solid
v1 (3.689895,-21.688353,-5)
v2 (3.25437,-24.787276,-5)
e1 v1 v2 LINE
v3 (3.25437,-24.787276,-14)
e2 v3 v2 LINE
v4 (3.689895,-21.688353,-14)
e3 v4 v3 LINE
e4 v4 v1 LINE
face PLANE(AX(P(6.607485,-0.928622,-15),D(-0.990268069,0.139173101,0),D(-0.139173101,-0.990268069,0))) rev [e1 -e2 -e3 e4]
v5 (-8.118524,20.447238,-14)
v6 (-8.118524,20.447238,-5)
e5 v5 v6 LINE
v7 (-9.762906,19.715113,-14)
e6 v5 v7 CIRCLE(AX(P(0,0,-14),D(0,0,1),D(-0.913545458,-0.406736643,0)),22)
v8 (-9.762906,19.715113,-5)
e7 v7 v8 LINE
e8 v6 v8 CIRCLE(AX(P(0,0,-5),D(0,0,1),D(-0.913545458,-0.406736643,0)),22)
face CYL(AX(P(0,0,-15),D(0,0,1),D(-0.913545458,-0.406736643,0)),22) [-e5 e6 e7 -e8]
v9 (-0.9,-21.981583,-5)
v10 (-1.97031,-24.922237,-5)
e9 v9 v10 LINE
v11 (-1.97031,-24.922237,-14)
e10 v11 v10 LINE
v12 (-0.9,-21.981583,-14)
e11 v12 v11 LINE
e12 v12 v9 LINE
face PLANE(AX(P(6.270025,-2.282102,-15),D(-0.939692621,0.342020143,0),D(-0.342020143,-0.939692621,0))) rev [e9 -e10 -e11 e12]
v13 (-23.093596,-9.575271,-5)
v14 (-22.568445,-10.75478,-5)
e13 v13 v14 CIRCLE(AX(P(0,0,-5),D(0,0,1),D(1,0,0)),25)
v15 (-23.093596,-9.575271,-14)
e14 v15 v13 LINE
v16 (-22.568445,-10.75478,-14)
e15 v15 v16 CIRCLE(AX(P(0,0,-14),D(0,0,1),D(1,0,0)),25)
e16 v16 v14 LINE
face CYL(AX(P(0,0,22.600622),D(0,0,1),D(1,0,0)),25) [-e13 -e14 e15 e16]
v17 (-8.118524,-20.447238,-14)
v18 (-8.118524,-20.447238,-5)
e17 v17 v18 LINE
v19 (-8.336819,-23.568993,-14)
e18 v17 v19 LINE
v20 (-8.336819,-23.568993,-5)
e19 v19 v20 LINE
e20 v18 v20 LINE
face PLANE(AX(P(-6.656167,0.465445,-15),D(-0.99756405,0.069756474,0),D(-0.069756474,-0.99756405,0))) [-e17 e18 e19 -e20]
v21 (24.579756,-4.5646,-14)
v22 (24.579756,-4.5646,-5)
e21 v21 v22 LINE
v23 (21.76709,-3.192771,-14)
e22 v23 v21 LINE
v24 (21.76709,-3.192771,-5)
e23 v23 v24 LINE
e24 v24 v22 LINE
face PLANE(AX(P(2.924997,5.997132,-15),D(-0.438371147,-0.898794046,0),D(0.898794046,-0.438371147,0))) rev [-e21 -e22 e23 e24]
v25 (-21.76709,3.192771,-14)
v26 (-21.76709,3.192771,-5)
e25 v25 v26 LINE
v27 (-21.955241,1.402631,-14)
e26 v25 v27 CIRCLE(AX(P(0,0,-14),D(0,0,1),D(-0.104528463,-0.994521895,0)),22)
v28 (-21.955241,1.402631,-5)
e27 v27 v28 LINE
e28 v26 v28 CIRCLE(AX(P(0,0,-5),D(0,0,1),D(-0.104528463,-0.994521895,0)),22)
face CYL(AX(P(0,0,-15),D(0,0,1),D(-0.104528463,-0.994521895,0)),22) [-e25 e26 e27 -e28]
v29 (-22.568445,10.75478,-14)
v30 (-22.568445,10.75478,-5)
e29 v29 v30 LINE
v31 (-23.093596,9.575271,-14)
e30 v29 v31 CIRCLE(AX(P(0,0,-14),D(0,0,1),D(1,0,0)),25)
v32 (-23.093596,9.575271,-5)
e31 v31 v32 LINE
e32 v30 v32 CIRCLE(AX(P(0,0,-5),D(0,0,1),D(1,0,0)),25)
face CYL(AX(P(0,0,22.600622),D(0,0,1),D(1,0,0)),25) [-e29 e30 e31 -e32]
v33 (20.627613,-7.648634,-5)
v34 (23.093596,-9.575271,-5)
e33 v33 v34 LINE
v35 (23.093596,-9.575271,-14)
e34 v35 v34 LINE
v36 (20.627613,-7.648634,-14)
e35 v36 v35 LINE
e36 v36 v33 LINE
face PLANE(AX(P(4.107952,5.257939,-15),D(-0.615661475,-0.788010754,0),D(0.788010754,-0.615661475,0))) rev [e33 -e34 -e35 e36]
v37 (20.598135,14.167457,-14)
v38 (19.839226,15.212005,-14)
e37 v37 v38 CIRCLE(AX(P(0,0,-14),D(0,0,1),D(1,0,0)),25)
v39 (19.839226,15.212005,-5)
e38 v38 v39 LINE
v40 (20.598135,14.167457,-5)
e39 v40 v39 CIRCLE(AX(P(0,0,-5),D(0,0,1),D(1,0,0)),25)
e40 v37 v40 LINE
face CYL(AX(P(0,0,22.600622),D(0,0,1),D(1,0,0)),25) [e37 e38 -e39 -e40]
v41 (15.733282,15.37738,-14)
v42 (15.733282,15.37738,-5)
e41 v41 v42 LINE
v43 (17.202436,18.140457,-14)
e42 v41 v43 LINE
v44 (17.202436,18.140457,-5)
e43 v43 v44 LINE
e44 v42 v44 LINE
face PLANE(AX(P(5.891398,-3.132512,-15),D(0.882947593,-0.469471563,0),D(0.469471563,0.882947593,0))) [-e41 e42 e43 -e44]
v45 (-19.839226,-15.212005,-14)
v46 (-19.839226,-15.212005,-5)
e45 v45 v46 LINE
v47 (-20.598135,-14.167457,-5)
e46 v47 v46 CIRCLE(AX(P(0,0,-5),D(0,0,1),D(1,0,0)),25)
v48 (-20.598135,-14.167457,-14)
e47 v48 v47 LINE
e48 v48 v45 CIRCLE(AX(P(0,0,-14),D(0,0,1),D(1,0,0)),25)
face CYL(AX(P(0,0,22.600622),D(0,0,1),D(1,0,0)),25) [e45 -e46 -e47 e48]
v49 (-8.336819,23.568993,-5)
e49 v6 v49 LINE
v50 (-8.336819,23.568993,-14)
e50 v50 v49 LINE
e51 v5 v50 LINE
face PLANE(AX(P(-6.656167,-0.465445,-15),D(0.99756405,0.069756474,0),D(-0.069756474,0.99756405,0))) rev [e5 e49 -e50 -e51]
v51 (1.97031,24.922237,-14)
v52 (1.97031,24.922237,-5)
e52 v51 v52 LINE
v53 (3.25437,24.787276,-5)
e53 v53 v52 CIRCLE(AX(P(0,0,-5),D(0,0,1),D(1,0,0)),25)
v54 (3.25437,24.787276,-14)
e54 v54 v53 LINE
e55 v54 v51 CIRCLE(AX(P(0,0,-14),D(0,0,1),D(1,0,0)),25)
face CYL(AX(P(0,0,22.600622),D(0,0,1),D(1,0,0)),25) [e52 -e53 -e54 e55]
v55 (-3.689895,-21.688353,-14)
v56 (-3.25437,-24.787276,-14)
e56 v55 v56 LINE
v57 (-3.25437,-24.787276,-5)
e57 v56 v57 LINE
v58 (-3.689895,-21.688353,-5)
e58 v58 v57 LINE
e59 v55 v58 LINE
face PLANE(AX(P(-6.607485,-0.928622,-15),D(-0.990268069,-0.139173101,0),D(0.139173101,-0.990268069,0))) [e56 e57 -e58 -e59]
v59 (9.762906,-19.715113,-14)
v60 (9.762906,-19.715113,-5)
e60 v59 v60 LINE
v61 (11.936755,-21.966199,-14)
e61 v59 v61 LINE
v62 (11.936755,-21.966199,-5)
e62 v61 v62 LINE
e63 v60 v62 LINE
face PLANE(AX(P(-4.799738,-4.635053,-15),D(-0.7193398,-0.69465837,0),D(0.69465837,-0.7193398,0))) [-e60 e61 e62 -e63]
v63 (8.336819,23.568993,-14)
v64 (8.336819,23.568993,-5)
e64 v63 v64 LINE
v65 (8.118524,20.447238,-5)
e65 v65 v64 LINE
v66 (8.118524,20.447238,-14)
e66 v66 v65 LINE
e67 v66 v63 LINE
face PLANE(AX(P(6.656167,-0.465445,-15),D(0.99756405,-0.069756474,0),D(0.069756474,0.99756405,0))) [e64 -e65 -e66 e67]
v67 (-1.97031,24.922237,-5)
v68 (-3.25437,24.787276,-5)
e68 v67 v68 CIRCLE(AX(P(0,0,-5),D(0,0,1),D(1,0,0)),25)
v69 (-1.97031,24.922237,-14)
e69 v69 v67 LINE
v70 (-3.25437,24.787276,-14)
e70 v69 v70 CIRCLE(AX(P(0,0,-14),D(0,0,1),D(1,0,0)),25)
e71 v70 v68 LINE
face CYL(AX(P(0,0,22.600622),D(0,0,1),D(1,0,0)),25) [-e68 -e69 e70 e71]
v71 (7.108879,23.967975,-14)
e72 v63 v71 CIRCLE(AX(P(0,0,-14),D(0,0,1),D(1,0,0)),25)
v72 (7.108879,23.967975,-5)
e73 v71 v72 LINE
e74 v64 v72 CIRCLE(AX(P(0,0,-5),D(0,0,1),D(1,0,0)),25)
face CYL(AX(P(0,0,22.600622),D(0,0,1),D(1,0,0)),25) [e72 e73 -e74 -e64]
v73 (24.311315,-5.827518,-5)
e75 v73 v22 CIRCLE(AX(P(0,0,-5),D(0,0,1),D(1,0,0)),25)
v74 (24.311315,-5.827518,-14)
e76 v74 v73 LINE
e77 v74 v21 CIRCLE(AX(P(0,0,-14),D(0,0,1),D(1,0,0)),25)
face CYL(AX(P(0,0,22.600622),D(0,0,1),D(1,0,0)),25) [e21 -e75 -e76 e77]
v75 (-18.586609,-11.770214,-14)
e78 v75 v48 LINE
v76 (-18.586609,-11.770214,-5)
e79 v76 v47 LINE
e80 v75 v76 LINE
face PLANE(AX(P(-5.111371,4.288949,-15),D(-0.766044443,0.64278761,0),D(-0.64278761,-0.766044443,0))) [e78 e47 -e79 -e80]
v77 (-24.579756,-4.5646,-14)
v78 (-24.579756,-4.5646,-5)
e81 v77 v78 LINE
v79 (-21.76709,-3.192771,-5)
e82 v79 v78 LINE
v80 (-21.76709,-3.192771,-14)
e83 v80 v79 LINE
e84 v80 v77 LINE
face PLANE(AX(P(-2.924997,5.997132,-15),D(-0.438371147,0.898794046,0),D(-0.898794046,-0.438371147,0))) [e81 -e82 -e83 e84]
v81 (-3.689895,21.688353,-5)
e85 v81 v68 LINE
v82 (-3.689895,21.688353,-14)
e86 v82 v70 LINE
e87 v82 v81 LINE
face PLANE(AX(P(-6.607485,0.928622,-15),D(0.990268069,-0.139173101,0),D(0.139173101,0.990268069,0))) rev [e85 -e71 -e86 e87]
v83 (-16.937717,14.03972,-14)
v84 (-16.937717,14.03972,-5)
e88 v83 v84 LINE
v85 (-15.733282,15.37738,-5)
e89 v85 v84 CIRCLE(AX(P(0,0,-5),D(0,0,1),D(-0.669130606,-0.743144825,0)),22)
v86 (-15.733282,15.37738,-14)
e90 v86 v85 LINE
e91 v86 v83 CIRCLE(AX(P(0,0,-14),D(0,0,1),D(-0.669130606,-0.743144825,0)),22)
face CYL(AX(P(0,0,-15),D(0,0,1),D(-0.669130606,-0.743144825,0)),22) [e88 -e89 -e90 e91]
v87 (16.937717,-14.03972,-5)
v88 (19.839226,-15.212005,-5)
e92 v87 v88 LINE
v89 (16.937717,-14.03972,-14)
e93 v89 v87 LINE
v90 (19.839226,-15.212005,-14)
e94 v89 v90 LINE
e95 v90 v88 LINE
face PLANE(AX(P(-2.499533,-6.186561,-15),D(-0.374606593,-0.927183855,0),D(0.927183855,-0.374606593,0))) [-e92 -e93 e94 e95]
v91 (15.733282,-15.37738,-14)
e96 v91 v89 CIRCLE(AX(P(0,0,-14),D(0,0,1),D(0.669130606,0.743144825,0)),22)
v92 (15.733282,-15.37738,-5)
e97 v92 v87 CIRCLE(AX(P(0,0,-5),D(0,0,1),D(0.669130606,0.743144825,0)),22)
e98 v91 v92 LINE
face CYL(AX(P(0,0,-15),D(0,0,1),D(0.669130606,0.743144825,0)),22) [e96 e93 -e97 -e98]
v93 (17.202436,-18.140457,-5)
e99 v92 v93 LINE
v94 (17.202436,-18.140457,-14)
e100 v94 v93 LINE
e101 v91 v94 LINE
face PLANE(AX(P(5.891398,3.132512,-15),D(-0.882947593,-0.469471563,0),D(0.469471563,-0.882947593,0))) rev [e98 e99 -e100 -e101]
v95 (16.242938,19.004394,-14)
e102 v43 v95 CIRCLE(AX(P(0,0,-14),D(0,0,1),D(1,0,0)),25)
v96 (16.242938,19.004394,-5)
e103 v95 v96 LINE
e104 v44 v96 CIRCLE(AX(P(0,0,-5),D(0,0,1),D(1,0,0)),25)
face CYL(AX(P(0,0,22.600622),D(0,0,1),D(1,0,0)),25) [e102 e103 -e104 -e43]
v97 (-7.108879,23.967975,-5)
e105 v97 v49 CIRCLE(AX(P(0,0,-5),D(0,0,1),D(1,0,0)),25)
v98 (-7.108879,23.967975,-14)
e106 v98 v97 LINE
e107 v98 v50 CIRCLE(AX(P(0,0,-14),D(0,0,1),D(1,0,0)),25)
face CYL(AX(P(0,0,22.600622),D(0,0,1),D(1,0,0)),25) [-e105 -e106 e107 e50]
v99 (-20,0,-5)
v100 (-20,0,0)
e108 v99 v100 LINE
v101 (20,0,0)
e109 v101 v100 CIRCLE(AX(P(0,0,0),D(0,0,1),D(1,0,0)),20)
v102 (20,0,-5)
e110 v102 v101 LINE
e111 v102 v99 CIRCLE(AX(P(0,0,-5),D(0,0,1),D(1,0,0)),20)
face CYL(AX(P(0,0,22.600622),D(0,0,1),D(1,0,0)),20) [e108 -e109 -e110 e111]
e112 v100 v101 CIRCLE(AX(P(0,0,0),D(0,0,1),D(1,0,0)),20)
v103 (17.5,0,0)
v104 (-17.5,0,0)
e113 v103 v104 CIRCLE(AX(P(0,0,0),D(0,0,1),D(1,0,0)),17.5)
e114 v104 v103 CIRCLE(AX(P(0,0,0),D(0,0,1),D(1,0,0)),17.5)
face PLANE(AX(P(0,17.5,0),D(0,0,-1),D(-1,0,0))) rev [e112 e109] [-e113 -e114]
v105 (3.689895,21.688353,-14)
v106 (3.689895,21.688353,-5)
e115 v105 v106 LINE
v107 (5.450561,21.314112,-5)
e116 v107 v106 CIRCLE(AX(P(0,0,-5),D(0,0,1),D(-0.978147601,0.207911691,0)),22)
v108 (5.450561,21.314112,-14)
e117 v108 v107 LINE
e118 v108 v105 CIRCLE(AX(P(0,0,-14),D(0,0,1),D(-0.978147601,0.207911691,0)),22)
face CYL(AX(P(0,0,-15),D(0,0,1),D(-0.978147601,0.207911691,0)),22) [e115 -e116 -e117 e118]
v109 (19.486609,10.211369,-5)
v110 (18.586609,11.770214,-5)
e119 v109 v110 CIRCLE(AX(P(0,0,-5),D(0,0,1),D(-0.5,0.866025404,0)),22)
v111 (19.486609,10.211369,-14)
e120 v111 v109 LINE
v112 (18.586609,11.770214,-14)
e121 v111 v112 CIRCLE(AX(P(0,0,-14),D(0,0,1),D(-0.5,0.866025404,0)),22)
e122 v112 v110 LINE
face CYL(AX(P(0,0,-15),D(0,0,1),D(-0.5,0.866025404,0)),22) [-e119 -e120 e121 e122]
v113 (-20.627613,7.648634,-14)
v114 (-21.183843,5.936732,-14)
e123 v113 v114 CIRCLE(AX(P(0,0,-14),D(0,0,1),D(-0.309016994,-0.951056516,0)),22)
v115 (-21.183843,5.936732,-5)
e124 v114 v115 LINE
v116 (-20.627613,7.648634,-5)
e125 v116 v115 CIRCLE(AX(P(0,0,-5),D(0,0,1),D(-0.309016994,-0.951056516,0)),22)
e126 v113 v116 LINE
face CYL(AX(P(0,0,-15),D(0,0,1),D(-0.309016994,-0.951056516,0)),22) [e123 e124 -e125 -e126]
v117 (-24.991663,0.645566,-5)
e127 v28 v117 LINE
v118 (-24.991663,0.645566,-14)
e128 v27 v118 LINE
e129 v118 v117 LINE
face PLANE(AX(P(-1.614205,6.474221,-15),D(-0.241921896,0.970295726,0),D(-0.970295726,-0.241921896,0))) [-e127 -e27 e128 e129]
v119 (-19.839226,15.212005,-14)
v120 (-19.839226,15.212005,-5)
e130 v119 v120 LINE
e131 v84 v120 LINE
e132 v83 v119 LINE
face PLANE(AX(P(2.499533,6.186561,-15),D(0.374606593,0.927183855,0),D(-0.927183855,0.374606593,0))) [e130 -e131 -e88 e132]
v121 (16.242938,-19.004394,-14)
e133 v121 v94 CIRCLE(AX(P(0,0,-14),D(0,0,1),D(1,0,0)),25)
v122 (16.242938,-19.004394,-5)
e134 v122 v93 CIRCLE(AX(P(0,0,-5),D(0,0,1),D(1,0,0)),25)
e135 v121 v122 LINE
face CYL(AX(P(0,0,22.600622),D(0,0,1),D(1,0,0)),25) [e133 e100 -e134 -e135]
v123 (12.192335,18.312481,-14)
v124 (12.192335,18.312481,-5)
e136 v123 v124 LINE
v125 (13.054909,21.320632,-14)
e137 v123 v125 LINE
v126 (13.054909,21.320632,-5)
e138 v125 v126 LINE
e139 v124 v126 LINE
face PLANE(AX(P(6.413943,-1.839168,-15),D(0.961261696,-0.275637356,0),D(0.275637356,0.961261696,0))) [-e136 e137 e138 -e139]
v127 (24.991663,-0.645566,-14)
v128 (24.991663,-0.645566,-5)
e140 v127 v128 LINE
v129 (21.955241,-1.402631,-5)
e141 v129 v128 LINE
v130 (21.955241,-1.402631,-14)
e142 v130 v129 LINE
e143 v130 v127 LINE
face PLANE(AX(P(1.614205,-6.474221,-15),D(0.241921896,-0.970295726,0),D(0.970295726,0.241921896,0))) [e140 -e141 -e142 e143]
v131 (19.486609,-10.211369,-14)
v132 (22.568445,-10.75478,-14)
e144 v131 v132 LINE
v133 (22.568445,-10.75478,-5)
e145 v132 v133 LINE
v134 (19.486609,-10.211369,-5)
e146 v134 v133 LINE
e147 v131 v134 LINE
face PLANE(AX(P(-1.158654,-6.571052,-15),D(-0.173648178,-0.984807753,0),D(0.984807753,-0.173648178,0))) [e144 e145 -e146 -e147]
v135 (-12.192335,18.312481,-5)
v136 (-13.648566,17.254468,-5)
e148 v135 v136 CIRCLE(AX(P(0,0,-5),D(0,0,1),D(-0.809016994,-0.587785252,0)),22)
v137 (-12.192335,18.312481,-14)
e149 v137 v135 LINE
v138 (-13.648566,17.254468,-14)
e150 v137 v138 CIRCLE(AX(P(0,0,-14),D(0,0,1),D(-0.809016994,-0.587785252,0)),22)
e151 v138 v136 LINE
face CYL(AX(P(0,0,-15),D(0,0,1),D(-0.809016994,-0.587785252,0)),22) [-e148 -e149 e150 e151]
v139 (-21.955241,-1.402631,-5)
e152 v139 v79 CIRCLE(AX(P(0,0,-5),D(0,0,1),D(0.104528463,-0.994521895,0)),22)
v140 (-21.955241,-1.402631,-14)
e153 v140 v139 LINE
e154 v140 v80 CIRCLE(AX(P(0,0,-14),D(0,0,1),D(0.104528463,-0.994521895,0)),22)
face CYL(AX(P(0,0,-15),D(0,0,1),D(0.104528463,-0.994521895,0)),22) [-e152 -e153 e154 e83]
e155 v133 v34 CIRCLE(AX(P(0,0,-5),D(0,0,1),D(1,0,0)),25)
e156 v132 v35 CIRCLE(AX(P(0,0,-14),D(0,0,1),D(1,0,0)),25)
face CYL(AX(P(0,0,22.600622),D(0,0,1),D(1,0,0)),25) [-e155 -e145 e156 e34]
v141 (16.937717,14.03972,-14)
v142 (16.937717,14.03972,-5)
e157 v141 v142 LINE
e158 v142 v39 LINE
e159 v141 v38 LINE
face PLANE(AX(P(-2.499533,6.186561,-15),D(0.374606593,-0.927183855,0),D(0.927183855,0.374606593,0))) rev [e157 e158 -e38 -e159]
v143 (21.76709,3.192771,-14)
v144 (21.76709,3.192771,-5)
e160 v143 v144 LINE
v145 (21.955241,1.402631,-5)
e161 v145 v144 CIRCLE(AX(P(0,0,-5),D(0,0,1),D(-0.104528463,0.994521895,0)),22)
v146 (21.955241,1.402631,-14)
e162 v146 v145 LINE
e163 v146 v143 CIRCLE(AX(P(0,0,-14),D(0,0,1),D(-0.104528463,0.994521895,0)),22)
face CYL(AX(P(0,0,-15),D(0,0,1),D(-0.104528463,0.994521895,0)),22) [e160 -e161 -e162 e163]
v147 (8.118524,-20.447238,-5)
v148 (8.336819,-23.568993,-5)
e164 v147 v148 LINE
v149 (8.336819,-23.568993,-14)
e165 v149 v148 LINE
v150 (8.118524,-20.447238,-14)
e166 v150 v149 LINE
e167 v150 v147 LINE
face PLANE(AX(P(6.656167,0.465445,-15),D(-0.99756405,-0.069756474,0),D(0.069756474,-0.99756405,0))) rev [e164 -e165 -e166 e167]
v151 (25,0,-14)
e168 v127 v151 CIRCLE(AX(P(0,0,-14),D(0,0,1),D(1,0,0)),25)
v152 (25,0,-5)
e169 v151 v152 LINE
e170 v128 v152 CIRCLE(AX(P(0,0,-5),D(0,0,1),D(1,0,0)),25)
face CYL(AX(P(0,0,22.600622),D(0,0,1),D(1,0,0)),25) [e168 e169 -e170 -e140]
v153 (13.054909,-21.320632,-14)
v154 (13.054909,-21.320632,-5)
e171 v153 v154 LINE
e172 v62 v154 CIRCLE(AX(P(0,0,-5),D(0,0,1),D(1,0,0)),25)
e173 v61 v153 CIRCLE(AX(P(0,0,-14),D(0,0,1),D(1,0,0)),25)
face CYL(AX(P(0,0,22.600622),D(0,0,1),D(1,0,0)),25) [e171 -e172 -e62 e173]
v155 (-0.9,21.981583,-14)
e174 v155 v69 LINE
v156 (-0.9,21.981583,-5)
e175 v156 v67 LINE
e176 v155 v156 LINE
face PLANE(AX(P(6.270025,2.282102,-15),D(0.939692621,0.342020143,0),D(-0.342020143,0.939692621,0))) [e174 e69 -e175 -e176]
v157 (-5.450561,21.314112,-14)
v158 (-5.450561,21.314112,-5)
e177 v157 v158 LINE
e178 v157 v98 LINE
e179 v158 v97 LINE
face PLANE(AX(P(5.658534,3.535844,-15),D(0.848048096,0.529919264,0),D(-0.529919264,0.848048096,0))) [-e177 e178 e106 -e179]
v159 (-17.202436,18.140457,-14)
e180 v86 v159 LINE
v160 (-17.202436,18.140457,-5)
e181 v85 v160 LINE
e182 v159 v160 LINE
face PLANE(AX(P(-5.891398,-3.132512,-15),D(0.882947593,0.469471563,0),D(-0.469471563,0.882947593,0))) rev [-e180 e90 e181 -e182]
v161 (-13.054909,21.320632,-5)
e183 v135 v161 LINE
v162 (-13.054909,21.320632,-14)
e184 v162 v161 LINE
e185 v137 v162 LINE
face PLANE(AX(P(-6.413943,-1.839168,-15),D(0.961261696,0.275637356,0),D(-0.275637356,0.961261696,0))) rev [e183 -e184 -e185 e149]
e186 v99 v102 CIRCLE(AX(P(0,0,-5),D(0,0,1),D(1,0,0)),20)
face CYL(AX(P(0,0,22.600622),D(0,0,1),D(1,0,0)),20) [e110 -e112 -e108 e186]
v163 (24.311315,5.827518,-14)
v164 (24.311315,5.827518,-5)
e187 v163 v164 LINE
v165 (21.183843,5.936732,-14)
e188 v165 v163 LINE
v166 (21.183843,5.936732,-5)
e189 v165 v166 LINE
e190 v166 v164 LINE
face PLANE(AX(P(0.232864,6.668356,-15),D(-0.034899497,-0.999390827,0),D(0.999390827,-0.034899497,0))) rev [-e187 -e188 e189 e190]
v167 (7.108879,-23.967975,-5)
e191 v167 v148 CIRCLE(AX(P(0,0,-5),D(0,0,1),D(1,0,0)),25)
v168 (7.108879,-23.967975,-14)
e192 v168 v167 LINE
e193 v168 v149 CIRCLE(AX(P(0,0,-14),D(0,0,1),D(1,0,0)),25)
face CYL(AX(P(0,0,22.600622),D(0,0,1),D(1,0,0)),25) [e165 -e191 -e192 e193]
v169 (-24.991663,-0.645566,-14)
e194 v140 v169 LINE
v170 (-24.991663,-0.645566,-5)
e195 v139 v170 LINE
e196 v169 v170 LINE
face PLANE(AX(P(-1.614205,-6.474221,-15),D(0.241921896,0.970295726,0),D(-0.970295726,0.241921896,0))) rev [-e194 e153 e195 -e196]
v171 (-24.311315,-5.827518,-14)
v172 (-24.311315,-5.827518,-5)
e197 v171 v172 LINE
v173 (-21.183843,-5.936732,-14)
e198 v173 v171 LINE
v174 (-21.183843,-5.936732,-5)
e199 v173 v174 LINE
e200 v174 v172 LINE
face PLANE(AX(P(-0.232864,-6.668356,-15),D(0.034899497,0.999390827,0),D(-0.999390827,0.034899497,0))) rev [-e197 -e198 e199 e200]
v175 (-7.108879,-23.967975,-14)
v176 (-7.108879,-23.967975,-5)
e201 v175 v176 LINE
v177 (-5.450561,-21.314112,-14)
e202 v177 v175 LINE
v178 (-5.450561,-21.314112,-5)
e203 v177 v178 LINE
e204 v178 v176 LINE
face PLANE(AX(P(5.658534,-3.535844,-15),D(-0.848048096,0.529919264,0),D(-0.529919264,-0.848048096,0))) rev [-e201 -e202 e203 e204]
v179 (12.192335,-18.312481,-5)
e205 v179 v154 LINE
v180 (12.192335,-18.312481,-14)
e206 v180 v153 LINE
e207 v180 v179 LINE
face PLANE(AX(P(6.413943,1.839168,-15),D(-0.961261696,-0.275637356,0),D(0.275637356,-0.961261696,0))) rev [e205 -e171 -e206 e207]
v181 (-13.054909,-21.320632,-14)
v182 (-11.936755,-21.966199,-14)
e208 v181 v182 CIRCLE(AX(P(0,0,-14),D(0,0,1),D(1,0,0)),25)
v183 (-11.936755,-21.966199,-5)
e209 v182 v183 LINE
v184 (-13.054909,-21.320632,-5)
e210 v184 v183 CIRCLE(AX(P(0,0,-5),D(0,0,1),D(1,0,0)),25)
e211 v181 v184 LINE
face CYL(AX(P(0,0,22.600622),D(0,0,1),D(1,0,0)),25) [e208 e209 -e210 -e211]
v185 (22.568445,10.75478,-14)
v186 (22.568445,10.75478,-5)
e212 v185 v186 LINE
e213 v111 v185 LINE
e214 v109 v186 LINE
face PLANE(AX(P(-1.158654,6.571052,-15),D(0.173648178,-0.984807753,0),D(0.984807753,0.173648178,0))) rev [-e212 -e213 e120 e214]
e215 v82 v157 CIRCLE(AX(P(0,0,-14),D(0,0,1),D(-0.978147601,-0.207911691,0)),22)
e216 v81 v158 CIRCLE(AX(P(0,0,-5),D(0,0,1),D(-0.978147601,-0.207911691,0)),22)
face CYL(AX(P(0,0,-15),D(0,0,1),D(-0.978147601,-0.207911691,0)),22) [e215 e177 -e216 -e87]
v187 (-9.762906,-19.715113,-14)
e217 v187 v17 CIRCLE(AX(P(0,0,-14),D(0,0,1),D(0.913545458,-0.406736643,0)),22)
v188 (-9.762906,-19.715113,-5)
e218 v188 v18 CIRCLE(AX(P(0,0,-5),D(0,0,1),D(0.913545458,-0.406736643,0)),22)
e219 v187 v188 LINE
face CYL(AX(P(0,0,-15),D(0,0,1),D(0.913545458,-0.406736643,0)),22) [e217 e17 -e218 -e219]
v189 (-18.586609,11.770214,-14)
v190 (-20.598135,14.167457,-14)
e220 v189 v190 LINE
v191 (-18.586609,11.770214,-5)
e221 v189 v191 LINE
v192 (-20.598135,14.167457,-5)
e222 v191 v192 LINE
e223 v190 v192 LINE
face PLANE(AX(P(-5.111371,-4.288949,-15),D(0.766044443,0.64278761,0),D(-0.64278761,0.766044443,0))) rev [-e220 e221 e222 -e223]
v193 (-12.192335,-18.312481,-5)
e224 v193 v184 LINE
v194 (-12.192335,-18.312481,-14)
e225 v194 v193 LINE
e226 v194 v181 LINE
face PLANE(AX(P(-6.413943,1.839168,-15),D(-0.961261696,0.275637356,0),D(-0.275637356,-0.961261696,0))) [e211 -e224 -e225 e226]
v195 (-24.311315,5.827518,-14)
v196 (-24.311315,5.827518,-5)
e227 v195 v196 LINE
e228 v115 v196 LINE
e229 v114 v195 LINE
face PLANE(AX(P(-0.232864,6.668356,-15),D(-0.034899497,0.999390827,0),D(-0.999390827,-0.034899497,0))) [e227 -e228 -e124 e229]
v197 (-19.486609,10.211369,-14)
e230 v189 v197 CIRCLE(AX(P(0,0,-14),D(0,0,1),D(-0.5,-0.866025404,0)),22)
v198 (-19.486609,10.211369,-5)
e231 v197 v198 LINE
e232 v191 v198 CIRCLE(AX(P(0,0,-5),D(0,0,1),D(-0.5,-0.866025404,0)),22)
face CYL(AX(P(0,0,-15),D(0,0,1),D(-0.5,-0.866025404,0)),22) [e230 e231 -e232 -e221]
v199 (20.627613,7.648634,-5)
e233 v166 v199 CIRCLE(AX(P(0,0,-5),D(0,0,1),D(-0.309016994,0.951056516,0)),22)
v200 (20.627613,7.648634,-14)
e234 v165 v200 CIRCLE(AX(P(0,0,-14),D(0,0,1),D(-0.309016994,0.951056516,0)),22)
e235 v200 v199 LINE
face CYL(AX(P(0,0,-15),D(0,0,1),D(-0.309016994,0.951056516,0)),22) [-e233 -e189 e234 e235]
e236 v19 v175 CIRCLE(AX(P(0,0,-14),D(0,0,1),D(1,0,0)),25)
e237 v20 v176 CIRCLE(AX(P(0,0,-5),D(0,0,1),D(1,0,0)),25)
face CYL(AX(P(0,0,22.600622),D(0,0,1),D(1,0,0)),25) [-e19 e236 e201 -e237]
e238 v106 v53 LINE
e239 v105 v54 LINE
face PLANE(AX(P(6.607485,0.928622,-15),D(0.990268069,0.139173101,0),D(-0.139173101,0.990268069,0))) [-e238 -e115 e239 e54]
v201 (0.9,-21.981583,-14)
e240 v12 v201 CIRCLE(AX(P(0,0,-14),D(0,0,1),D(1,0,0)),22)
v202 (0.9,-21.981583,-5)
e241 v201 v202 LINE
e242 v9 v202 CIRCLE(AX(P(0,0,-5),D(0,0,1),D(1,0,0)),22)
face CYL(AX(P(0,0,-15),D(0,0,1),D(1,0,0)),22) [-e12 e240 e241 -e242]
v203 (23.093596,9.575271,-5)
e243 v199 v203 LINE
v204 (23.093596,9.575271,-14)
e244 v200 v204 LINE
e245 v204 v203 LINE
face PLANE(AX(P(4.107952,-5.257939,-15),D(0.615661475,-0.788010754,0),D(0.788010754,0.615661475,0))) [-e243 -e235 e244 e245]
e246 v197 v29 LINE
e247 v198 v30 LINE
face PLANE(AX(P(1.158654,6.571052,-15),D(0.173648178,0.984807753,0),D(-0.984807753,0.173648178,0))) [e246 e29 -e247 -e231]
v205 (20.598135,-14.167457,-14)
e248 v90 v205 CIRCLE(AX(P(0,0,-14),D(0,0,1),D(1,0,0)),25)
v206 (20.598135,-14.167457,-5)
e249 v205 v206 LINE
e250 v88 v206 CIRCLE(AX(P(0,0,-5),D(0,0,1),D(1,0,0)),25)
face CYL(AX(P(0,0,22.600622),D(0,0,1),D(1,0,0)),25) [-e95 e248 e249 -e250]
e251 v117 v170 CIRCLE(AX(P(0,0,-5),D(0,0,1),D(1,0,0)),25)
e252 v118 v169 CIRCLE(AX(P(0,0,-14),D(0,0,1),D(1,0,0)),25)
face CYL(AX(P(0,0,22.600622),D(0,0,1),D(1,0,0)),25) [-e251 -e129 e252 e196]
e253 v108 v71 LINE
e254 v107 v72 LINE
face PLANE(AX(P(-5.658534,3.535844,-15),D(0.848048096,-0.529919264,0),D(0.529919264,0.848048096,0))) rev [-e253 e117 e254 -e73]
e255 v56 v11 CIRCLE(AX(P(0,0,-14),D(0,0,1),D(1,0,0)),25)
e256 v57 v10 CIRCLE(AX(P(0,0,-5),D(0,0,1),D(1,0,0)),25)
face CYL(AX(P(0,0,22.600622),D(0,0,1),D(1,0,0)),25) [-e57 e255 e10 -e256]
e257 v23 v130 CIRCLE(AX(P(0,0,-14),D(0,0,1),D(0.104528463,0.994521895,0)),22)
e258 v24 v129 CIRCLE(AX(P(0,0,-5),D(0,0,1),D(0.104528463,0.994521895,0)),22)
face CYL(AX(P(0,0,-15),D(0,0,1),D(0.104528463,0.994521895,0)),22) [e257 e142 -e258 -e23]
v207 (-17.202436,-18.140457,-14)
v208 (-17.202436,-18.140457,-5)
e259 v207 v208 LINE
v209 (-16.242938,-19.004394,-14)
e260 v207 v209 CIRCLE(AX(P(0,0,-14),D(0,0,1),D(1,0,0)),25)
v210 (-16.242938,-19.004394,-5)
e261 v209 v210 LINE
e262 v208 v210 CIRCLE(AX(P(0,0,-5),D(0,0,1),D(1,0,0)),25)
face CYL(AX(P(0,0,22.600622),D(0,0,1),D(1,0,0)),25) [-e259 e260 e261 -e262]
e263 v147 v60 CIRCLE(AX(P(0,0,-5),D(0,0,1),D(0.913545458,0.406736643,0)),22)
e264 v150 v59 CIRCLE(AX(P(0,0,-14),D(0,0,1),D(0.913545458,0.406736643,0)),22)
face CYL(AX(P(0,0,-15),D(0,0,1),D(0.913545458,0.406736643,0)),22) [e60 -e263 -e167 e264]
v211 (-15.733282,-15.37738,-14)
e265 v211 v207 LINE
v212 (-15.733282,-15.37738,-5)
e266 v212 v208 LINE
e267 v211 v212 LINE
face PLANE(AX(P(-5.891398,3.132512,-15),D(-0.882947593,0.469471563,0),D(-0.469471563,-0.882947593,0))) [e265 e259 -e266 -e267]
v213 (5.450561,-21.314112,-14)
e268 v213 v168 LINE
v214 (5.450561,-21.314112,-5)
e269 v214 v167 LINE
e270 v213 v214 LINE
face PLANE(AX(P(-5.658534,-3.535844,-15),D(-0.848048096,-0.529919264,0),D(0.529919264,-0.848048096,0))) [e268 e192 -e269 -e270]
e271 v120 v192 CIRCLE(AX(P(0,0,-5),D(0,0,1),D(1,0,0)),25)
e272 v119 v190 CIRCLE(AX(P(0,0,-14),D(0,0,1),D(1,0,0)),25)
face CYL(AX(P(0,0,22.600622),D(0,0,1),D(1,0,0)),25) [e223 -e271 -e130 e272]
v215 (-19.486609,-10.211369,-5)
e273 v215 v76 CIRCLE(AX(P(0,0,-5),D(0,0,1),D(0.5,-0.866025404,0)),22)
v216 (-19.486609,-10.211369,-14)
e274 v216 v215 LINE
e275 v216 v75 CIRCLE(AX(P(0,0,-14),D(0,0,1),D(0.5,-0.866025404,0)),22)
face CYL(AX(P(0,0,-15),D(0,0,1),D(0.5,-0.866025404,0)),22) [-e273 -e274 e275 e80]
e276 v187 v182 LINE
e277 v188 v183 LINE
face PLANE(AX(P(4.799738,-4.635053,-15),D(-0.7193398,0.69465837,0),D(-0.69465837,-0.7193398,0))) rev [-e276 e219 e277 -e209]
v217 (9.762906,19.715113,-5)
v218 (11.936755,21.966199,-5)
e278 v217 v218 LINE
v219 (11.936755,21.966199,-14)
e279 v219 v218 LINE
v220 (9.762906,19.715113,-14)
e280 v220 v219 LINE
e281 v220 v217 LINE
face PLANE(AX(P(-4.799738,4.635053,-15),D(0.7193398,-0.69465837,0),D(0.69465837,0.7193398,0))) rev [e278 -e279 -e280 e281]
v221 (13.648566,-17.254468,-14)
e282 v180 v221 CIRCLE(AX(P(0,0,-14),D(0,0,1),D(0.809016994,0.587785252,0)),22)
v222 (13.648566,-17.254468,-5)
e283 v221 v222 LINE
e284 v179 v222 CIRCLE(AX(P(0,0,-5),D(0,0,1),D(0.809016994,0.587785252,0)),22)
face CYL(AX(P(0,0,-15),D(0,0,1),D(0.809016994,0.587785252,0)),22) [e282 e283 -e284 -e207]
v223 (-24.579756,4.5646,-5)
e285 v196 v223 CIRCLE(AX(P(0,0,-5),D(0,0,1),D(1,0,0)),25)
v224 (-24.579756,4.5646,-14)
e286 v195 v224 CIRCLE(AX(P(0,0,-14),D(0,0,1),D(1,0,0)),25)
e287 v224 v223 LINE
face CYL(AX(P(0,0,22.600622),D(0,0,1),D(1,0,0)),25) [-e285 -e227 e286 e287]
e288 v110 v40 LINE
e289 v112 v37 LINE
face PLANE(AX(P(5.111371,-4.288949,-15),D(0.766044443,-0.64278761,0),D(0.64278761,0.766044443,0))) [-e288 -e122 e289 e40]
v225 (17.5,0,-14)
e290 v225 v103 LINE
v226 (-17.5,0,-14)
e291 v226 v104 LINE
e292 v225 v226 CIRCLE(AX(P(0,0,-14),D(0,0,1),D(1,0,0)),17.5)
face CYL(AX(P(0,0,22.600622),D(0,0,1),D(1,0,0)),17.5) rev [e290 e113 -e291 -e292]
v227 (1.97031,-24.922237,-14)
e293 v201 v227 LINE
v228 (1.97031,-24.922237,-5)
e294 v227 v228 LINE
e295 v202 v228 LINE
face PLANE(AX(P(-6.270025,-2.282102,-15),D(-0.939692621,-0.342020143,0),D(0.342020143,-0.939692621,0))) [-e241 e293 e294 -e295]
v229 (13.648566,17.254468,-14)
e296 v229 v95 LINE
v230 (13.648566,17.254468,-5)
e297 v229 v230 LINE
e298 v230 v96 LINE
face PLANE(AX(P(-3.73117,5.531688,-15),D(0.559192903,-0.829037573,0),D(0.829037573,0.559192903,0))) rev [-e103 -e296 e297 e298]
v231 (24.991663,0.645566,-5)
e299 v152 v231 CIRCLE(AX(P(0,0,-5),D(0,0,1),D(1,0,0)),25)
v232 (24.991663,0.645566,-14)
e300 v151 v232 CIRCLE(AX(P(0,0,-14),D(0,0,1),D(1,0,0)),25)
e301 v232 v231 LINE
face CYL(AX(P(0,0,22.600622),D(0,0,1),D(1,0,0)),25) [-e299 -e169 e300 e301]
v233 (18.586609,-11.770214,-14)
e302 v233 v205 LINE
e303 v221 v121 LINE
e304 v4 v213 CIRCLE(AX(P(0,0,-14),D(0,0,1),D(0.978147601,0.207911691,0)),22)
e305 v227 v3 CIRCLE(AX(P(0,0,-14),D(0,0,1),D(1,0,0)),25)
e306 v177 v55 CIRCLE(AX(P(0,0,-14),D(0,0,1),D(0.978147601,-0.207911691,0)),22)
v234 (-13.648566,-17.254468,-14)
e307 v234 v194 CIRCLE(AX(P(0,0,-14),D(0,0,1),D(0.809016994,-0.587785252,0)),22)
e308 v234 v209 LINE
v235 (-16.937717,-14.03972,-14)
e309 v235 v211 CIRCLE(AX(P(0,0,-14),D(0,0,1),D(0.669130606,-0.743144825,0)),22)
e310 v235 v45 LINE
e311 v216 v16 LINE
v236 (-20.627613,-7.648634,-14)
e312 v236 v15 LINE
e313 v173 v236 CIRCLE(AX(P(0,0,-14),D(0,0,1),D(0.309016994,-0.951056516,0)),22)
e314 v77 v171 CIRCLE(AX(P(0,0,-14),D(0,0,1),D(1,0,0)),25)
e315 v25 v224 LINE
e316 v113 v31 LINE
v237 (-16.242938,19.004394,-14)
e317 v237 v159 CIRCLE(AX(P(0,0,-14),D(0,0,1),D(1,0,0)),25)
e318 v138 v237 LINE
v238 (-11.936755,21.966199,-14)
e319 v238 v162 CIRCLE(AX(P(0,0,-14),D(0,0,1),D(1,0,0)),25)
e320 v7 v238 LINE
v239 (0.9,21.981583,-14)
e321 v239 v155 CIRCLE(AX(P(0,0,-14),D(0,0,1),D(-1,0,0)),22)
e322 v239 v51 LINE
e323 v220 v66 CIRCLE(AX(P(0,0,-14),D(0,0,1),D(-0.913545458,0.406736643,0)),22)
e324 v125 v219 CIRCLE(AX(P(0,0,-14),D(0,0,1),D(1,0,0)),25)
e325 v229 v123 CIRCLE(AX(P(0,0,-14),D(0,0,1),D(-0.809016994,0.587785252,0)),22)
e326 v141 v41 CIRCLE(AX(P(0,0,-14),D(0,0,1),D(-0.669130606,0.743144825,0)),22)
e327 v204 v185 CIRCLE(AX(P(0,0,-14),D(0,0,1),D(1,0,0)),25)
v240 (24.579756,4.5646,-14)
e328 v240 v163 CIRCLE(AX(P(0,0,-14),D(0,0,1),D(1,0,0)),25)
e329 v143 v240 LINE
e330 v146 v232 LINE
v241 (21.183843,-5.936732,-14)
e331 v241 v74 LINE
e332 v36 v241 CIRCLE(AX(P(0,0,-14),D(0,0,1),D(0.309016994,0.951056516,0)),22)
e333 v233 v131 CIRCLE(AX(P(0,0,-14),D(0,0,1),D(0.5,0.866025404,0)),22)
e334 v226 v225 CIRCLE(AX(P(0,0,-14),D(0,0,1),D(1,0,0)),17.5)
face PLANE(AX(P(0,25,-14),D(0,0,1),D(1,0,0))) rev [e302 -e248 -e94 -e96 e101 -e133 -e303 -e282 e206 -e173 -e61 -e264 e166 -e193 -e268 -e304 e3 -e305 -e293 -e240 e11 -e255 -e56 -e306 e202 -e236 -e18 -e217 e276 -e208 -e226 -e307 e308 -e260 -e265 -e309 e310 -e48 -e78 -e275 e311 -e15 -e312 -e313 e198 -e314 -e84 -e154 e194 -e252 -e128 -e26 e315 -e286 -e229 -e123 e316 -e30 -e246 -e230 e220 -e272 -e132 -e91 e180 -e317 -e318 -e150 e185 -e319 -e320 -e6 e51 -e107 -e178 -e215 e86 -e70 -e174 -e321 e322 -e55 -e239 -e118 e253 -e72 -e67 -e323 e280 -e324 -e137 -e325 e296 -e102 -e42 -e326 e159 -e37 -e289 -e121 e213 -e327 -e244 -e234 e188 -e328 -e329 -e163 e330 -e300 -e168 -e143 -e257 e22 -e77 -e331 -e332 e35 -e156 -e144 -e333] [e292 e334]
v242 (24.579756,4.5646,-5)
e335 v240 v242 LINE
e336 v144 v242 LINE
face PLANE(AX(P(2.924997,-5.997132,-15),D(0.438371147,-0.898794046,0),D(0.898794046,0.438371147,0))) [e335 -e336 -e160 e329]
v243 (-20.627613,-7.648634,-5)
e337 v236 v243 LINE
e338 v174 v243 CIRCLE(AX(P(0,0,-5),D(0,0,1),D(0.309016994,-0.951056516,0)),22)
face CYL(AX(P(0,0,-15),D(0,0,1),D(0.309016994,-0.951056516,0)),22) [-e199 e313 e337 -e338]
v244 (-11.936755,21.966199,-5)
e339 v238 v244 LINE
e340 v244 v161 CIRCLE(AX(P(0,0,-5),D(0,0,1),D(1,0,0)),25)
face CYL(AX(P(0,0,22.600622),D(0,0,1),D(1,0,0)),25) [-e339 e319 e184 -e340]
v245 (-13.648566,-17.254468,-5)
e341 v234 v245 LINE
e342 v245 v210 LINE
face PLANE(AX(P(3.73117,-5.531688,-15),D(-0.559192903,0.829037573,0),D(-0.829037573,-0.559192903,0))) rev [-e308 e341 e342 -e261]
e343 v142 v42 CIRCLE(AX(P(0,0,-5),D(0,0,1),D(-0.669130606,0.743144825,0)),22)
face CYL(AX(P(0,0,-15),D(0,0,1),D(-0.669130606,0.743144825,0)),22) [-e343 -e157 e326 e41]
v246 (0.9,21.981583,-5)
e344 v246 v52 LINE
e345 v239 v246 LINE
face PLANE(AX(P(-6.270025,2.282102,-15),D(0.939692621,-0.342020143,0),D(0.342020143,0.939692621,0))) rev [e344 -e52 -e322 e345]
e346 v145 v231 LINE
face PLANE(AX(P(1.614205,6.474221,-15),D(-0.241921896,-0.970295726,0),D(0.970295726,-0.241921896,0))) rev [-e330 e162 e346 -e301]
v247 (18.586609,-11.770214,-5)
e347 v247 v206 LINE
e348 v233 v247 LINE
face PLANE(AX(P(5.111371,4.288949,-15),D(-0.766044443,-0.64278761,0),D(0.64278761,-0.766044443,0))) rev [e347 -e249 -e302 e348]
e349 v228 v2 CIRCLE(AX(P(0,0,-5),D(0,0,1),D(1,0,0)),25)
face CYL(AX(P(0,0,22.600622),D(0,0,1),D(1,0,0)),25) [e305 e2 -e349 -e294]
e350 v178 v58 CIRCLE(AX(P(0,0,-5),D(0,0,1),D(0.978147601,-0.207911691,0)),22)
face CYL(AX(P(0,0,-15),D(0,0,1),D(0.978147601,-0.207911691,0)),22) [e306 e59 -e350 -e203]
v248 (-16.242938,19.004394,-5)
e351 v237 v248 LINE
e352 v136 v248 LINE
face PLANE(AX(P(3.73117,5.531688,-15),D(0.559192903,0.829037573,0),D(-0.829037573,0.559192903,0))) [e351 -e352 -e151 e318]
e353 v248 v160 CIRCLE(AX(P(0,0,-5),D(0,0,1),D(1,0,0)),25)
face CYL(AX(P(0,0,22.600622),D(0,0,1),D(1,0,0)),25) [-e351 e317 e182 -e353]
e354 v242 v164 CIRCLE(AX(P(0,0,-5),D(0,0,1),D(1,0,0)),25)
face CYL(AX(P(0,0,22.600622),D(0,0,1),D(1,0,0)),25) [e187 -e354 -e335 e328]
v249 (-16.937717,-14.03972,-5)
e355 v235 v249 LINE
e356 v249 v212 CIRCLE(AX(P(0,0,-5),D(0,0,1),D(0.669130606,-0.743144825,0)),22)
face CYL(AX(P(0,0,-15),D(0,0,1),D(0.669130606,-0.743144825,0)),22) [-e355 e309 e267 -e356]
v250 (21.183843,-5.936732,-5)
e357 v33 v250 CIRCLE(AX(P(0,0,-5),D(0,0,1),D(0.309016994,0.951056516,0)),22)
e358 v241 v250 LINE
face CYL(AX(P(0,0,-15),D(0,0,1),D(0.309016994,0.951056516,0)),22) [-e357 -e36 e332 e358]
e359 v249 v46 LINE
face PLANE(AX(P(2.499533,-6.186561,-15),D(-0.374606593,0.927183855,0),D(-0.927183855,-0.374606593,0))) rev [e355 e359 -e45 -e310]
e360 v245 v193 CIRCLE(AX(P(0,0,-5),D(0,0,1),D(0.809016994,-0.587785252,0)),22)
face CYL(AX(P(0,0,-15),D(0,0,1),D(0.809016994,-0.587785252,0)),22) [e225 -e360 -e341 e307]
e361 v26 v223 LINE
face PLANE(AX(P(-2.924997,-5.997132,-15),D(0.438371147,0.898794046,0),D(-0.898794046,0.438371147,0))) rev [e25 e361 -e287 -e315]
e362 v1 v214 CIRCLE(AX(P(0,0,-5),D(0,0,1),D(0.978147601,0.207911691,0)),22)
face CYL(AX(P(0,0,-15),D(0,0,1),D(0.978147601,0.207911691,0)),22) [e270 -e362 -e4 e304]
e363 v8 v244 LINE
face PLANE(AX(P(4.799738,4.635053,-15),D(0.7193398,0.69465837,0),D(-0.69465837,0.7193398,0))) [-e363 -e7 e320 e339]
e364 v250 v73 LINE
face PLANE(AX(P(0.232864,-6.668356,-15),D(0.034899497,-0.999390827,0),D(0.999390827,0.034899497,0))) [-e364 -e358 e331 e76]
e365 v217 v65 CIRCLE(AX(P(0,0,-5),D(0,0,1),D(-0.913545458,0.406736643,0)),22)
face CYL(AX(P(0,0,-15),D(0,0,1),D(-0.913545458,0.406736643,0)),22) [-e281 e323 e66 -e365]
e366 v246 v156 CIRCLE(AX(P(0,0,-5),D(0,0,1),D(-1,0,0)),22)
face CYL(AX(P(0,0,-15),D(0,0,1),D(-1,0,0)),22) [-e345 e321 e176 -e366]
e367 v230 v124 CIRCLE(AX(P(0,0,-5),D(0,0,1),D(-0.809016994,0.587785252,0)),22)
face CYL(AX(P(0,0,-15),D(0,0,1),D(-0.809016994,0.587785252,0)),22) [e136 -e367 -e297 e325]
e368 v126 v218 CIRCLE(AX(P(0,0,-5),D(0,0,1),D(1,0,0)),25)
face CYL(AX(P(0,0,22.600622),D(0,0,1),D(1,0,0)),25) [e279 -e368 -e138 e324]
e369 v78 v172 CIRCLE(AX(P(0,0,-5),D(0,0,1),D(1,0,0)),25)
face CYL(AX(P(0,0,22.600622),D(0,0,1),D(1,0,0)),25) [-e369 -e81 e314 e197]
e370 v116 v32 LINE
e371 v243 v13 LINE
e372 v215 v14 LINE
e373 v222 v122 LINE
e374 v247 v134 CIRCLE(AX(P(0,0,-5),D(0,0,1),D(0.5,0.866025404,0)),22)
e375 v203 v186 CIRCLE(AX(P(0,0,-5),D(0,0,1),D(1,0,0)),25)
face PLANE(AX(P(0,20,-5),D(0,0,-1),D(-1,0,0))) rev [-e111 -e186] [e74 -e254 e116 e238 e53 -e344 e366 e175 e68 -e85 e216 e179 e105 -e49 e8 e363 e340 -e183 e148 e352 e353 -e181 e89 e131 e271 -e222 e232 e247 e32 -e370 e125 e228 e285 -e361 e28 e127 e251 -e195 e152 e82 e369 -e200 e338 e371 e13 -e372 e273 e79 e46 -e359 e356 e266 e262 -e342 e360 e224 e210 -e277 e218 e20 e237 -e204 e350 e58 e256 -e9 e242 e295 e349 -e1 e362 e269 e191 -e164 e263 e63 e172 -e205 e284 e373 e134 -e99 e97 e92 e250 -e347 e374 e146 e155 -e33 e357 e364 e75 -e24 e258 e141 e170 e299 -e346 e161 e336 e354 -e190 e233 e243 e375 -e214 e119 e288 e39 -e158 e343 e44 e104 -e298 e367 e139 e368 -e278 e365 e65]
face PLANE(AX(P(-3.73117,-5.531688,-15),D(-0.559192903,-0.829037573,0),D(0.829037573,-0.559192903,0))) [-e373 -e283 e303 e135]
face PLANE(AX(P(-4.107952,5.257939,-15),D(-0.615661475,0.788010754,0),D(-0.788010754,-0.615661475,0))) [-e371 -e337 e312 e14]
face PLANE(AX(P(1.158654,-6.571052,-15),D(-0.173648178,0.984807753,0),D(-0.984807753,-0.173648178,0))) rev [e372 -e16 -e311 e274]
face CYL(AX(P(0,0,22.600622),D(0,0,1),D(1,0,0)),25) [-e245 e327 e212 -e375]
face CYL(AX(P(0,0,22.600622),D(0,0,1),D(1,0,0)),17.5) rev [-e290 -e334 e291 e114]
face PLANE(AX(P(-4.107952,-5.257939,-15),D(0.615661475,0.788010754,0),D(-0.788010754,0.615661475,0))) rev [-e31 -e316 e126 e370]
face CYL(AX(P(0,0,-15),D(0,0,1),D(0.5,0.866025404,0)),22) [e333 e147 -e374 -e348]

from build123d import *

# Parameters (mm, degrees)
CUT_EXTRUDE1_START = -10
CUT_EXTRUDE1_DEPTH = 10
CIRPATTERN1_COUNT  = 30


with BuildPart() as part:
    # Sketch1 → Revolve1 (revolve)
    with BuildSketch(Plane(origin=(0, 0, 0), x_dir=(0, 0, -1), z_dir=(1, 0, 0)), mode=Mode.PRIVATE) as revolve1_sk:
        Polygon((0, 17.5), (0, 20), (5, 20), (5, 25), (14, 25), (14, 17.5), align=None)
    revolve(revolve1_sk.sketch.rotate(Axis((0, 0, 22.600622446), (0, 0, -1)), 90), axis=Axis((0, 0, 22.600622446), (0, 0, -1)))

    # Sketch2 → Cut-Extrude1 (cut)
    with BuildSketch(Plane.XY.offset(-5).offset(CUT_EXTRUDE1_START)):
        with BuildLine():
            Line((-0.9, -21.9815832), (-1.970310308, -24.922236603))
            ThreePointArc((-1.970310308, -24.922236603), (-0.985922139, -24.980551586), (0, -25))
            Line((0, -25), (0, -22))
            ThreePointArc((0, -22), (-0.450094206, -21.995395318), (-0.9, -21.9815832))
        make_face()
        with BuildLine():
            ThreePointArc((0.9, -21.9815832), (0.450094206, -21.995395318), (0, -22))
            Line((0, -22), (0, -25))
            ThreePointArc((0, -25), (0.985922139, -24.980551586), (1.970310308, -24.922236603))
            Line((1.970310308, -24.922236603), (0.9, -21.9815832))
        make_face()
    cut_extrude1 = extrude(amount=CUT_EXTRUDE1_DEPTH, mode=Mode.SUBTRACT)

    # CirPattern1: Cut-Extrude1 ×30 about axis
    cirpattern1_axis = Axis((0, 0, 0), (0, 0, 1))
    for i in range(1, CIRPATTERN1_COUNT):
        add(cut_extrude1.rotate(cirpattern1_axis, i * 360 / CIRPATTERN1_COUNT), mode=Mode.SUBTRACT)


solid = part.part
